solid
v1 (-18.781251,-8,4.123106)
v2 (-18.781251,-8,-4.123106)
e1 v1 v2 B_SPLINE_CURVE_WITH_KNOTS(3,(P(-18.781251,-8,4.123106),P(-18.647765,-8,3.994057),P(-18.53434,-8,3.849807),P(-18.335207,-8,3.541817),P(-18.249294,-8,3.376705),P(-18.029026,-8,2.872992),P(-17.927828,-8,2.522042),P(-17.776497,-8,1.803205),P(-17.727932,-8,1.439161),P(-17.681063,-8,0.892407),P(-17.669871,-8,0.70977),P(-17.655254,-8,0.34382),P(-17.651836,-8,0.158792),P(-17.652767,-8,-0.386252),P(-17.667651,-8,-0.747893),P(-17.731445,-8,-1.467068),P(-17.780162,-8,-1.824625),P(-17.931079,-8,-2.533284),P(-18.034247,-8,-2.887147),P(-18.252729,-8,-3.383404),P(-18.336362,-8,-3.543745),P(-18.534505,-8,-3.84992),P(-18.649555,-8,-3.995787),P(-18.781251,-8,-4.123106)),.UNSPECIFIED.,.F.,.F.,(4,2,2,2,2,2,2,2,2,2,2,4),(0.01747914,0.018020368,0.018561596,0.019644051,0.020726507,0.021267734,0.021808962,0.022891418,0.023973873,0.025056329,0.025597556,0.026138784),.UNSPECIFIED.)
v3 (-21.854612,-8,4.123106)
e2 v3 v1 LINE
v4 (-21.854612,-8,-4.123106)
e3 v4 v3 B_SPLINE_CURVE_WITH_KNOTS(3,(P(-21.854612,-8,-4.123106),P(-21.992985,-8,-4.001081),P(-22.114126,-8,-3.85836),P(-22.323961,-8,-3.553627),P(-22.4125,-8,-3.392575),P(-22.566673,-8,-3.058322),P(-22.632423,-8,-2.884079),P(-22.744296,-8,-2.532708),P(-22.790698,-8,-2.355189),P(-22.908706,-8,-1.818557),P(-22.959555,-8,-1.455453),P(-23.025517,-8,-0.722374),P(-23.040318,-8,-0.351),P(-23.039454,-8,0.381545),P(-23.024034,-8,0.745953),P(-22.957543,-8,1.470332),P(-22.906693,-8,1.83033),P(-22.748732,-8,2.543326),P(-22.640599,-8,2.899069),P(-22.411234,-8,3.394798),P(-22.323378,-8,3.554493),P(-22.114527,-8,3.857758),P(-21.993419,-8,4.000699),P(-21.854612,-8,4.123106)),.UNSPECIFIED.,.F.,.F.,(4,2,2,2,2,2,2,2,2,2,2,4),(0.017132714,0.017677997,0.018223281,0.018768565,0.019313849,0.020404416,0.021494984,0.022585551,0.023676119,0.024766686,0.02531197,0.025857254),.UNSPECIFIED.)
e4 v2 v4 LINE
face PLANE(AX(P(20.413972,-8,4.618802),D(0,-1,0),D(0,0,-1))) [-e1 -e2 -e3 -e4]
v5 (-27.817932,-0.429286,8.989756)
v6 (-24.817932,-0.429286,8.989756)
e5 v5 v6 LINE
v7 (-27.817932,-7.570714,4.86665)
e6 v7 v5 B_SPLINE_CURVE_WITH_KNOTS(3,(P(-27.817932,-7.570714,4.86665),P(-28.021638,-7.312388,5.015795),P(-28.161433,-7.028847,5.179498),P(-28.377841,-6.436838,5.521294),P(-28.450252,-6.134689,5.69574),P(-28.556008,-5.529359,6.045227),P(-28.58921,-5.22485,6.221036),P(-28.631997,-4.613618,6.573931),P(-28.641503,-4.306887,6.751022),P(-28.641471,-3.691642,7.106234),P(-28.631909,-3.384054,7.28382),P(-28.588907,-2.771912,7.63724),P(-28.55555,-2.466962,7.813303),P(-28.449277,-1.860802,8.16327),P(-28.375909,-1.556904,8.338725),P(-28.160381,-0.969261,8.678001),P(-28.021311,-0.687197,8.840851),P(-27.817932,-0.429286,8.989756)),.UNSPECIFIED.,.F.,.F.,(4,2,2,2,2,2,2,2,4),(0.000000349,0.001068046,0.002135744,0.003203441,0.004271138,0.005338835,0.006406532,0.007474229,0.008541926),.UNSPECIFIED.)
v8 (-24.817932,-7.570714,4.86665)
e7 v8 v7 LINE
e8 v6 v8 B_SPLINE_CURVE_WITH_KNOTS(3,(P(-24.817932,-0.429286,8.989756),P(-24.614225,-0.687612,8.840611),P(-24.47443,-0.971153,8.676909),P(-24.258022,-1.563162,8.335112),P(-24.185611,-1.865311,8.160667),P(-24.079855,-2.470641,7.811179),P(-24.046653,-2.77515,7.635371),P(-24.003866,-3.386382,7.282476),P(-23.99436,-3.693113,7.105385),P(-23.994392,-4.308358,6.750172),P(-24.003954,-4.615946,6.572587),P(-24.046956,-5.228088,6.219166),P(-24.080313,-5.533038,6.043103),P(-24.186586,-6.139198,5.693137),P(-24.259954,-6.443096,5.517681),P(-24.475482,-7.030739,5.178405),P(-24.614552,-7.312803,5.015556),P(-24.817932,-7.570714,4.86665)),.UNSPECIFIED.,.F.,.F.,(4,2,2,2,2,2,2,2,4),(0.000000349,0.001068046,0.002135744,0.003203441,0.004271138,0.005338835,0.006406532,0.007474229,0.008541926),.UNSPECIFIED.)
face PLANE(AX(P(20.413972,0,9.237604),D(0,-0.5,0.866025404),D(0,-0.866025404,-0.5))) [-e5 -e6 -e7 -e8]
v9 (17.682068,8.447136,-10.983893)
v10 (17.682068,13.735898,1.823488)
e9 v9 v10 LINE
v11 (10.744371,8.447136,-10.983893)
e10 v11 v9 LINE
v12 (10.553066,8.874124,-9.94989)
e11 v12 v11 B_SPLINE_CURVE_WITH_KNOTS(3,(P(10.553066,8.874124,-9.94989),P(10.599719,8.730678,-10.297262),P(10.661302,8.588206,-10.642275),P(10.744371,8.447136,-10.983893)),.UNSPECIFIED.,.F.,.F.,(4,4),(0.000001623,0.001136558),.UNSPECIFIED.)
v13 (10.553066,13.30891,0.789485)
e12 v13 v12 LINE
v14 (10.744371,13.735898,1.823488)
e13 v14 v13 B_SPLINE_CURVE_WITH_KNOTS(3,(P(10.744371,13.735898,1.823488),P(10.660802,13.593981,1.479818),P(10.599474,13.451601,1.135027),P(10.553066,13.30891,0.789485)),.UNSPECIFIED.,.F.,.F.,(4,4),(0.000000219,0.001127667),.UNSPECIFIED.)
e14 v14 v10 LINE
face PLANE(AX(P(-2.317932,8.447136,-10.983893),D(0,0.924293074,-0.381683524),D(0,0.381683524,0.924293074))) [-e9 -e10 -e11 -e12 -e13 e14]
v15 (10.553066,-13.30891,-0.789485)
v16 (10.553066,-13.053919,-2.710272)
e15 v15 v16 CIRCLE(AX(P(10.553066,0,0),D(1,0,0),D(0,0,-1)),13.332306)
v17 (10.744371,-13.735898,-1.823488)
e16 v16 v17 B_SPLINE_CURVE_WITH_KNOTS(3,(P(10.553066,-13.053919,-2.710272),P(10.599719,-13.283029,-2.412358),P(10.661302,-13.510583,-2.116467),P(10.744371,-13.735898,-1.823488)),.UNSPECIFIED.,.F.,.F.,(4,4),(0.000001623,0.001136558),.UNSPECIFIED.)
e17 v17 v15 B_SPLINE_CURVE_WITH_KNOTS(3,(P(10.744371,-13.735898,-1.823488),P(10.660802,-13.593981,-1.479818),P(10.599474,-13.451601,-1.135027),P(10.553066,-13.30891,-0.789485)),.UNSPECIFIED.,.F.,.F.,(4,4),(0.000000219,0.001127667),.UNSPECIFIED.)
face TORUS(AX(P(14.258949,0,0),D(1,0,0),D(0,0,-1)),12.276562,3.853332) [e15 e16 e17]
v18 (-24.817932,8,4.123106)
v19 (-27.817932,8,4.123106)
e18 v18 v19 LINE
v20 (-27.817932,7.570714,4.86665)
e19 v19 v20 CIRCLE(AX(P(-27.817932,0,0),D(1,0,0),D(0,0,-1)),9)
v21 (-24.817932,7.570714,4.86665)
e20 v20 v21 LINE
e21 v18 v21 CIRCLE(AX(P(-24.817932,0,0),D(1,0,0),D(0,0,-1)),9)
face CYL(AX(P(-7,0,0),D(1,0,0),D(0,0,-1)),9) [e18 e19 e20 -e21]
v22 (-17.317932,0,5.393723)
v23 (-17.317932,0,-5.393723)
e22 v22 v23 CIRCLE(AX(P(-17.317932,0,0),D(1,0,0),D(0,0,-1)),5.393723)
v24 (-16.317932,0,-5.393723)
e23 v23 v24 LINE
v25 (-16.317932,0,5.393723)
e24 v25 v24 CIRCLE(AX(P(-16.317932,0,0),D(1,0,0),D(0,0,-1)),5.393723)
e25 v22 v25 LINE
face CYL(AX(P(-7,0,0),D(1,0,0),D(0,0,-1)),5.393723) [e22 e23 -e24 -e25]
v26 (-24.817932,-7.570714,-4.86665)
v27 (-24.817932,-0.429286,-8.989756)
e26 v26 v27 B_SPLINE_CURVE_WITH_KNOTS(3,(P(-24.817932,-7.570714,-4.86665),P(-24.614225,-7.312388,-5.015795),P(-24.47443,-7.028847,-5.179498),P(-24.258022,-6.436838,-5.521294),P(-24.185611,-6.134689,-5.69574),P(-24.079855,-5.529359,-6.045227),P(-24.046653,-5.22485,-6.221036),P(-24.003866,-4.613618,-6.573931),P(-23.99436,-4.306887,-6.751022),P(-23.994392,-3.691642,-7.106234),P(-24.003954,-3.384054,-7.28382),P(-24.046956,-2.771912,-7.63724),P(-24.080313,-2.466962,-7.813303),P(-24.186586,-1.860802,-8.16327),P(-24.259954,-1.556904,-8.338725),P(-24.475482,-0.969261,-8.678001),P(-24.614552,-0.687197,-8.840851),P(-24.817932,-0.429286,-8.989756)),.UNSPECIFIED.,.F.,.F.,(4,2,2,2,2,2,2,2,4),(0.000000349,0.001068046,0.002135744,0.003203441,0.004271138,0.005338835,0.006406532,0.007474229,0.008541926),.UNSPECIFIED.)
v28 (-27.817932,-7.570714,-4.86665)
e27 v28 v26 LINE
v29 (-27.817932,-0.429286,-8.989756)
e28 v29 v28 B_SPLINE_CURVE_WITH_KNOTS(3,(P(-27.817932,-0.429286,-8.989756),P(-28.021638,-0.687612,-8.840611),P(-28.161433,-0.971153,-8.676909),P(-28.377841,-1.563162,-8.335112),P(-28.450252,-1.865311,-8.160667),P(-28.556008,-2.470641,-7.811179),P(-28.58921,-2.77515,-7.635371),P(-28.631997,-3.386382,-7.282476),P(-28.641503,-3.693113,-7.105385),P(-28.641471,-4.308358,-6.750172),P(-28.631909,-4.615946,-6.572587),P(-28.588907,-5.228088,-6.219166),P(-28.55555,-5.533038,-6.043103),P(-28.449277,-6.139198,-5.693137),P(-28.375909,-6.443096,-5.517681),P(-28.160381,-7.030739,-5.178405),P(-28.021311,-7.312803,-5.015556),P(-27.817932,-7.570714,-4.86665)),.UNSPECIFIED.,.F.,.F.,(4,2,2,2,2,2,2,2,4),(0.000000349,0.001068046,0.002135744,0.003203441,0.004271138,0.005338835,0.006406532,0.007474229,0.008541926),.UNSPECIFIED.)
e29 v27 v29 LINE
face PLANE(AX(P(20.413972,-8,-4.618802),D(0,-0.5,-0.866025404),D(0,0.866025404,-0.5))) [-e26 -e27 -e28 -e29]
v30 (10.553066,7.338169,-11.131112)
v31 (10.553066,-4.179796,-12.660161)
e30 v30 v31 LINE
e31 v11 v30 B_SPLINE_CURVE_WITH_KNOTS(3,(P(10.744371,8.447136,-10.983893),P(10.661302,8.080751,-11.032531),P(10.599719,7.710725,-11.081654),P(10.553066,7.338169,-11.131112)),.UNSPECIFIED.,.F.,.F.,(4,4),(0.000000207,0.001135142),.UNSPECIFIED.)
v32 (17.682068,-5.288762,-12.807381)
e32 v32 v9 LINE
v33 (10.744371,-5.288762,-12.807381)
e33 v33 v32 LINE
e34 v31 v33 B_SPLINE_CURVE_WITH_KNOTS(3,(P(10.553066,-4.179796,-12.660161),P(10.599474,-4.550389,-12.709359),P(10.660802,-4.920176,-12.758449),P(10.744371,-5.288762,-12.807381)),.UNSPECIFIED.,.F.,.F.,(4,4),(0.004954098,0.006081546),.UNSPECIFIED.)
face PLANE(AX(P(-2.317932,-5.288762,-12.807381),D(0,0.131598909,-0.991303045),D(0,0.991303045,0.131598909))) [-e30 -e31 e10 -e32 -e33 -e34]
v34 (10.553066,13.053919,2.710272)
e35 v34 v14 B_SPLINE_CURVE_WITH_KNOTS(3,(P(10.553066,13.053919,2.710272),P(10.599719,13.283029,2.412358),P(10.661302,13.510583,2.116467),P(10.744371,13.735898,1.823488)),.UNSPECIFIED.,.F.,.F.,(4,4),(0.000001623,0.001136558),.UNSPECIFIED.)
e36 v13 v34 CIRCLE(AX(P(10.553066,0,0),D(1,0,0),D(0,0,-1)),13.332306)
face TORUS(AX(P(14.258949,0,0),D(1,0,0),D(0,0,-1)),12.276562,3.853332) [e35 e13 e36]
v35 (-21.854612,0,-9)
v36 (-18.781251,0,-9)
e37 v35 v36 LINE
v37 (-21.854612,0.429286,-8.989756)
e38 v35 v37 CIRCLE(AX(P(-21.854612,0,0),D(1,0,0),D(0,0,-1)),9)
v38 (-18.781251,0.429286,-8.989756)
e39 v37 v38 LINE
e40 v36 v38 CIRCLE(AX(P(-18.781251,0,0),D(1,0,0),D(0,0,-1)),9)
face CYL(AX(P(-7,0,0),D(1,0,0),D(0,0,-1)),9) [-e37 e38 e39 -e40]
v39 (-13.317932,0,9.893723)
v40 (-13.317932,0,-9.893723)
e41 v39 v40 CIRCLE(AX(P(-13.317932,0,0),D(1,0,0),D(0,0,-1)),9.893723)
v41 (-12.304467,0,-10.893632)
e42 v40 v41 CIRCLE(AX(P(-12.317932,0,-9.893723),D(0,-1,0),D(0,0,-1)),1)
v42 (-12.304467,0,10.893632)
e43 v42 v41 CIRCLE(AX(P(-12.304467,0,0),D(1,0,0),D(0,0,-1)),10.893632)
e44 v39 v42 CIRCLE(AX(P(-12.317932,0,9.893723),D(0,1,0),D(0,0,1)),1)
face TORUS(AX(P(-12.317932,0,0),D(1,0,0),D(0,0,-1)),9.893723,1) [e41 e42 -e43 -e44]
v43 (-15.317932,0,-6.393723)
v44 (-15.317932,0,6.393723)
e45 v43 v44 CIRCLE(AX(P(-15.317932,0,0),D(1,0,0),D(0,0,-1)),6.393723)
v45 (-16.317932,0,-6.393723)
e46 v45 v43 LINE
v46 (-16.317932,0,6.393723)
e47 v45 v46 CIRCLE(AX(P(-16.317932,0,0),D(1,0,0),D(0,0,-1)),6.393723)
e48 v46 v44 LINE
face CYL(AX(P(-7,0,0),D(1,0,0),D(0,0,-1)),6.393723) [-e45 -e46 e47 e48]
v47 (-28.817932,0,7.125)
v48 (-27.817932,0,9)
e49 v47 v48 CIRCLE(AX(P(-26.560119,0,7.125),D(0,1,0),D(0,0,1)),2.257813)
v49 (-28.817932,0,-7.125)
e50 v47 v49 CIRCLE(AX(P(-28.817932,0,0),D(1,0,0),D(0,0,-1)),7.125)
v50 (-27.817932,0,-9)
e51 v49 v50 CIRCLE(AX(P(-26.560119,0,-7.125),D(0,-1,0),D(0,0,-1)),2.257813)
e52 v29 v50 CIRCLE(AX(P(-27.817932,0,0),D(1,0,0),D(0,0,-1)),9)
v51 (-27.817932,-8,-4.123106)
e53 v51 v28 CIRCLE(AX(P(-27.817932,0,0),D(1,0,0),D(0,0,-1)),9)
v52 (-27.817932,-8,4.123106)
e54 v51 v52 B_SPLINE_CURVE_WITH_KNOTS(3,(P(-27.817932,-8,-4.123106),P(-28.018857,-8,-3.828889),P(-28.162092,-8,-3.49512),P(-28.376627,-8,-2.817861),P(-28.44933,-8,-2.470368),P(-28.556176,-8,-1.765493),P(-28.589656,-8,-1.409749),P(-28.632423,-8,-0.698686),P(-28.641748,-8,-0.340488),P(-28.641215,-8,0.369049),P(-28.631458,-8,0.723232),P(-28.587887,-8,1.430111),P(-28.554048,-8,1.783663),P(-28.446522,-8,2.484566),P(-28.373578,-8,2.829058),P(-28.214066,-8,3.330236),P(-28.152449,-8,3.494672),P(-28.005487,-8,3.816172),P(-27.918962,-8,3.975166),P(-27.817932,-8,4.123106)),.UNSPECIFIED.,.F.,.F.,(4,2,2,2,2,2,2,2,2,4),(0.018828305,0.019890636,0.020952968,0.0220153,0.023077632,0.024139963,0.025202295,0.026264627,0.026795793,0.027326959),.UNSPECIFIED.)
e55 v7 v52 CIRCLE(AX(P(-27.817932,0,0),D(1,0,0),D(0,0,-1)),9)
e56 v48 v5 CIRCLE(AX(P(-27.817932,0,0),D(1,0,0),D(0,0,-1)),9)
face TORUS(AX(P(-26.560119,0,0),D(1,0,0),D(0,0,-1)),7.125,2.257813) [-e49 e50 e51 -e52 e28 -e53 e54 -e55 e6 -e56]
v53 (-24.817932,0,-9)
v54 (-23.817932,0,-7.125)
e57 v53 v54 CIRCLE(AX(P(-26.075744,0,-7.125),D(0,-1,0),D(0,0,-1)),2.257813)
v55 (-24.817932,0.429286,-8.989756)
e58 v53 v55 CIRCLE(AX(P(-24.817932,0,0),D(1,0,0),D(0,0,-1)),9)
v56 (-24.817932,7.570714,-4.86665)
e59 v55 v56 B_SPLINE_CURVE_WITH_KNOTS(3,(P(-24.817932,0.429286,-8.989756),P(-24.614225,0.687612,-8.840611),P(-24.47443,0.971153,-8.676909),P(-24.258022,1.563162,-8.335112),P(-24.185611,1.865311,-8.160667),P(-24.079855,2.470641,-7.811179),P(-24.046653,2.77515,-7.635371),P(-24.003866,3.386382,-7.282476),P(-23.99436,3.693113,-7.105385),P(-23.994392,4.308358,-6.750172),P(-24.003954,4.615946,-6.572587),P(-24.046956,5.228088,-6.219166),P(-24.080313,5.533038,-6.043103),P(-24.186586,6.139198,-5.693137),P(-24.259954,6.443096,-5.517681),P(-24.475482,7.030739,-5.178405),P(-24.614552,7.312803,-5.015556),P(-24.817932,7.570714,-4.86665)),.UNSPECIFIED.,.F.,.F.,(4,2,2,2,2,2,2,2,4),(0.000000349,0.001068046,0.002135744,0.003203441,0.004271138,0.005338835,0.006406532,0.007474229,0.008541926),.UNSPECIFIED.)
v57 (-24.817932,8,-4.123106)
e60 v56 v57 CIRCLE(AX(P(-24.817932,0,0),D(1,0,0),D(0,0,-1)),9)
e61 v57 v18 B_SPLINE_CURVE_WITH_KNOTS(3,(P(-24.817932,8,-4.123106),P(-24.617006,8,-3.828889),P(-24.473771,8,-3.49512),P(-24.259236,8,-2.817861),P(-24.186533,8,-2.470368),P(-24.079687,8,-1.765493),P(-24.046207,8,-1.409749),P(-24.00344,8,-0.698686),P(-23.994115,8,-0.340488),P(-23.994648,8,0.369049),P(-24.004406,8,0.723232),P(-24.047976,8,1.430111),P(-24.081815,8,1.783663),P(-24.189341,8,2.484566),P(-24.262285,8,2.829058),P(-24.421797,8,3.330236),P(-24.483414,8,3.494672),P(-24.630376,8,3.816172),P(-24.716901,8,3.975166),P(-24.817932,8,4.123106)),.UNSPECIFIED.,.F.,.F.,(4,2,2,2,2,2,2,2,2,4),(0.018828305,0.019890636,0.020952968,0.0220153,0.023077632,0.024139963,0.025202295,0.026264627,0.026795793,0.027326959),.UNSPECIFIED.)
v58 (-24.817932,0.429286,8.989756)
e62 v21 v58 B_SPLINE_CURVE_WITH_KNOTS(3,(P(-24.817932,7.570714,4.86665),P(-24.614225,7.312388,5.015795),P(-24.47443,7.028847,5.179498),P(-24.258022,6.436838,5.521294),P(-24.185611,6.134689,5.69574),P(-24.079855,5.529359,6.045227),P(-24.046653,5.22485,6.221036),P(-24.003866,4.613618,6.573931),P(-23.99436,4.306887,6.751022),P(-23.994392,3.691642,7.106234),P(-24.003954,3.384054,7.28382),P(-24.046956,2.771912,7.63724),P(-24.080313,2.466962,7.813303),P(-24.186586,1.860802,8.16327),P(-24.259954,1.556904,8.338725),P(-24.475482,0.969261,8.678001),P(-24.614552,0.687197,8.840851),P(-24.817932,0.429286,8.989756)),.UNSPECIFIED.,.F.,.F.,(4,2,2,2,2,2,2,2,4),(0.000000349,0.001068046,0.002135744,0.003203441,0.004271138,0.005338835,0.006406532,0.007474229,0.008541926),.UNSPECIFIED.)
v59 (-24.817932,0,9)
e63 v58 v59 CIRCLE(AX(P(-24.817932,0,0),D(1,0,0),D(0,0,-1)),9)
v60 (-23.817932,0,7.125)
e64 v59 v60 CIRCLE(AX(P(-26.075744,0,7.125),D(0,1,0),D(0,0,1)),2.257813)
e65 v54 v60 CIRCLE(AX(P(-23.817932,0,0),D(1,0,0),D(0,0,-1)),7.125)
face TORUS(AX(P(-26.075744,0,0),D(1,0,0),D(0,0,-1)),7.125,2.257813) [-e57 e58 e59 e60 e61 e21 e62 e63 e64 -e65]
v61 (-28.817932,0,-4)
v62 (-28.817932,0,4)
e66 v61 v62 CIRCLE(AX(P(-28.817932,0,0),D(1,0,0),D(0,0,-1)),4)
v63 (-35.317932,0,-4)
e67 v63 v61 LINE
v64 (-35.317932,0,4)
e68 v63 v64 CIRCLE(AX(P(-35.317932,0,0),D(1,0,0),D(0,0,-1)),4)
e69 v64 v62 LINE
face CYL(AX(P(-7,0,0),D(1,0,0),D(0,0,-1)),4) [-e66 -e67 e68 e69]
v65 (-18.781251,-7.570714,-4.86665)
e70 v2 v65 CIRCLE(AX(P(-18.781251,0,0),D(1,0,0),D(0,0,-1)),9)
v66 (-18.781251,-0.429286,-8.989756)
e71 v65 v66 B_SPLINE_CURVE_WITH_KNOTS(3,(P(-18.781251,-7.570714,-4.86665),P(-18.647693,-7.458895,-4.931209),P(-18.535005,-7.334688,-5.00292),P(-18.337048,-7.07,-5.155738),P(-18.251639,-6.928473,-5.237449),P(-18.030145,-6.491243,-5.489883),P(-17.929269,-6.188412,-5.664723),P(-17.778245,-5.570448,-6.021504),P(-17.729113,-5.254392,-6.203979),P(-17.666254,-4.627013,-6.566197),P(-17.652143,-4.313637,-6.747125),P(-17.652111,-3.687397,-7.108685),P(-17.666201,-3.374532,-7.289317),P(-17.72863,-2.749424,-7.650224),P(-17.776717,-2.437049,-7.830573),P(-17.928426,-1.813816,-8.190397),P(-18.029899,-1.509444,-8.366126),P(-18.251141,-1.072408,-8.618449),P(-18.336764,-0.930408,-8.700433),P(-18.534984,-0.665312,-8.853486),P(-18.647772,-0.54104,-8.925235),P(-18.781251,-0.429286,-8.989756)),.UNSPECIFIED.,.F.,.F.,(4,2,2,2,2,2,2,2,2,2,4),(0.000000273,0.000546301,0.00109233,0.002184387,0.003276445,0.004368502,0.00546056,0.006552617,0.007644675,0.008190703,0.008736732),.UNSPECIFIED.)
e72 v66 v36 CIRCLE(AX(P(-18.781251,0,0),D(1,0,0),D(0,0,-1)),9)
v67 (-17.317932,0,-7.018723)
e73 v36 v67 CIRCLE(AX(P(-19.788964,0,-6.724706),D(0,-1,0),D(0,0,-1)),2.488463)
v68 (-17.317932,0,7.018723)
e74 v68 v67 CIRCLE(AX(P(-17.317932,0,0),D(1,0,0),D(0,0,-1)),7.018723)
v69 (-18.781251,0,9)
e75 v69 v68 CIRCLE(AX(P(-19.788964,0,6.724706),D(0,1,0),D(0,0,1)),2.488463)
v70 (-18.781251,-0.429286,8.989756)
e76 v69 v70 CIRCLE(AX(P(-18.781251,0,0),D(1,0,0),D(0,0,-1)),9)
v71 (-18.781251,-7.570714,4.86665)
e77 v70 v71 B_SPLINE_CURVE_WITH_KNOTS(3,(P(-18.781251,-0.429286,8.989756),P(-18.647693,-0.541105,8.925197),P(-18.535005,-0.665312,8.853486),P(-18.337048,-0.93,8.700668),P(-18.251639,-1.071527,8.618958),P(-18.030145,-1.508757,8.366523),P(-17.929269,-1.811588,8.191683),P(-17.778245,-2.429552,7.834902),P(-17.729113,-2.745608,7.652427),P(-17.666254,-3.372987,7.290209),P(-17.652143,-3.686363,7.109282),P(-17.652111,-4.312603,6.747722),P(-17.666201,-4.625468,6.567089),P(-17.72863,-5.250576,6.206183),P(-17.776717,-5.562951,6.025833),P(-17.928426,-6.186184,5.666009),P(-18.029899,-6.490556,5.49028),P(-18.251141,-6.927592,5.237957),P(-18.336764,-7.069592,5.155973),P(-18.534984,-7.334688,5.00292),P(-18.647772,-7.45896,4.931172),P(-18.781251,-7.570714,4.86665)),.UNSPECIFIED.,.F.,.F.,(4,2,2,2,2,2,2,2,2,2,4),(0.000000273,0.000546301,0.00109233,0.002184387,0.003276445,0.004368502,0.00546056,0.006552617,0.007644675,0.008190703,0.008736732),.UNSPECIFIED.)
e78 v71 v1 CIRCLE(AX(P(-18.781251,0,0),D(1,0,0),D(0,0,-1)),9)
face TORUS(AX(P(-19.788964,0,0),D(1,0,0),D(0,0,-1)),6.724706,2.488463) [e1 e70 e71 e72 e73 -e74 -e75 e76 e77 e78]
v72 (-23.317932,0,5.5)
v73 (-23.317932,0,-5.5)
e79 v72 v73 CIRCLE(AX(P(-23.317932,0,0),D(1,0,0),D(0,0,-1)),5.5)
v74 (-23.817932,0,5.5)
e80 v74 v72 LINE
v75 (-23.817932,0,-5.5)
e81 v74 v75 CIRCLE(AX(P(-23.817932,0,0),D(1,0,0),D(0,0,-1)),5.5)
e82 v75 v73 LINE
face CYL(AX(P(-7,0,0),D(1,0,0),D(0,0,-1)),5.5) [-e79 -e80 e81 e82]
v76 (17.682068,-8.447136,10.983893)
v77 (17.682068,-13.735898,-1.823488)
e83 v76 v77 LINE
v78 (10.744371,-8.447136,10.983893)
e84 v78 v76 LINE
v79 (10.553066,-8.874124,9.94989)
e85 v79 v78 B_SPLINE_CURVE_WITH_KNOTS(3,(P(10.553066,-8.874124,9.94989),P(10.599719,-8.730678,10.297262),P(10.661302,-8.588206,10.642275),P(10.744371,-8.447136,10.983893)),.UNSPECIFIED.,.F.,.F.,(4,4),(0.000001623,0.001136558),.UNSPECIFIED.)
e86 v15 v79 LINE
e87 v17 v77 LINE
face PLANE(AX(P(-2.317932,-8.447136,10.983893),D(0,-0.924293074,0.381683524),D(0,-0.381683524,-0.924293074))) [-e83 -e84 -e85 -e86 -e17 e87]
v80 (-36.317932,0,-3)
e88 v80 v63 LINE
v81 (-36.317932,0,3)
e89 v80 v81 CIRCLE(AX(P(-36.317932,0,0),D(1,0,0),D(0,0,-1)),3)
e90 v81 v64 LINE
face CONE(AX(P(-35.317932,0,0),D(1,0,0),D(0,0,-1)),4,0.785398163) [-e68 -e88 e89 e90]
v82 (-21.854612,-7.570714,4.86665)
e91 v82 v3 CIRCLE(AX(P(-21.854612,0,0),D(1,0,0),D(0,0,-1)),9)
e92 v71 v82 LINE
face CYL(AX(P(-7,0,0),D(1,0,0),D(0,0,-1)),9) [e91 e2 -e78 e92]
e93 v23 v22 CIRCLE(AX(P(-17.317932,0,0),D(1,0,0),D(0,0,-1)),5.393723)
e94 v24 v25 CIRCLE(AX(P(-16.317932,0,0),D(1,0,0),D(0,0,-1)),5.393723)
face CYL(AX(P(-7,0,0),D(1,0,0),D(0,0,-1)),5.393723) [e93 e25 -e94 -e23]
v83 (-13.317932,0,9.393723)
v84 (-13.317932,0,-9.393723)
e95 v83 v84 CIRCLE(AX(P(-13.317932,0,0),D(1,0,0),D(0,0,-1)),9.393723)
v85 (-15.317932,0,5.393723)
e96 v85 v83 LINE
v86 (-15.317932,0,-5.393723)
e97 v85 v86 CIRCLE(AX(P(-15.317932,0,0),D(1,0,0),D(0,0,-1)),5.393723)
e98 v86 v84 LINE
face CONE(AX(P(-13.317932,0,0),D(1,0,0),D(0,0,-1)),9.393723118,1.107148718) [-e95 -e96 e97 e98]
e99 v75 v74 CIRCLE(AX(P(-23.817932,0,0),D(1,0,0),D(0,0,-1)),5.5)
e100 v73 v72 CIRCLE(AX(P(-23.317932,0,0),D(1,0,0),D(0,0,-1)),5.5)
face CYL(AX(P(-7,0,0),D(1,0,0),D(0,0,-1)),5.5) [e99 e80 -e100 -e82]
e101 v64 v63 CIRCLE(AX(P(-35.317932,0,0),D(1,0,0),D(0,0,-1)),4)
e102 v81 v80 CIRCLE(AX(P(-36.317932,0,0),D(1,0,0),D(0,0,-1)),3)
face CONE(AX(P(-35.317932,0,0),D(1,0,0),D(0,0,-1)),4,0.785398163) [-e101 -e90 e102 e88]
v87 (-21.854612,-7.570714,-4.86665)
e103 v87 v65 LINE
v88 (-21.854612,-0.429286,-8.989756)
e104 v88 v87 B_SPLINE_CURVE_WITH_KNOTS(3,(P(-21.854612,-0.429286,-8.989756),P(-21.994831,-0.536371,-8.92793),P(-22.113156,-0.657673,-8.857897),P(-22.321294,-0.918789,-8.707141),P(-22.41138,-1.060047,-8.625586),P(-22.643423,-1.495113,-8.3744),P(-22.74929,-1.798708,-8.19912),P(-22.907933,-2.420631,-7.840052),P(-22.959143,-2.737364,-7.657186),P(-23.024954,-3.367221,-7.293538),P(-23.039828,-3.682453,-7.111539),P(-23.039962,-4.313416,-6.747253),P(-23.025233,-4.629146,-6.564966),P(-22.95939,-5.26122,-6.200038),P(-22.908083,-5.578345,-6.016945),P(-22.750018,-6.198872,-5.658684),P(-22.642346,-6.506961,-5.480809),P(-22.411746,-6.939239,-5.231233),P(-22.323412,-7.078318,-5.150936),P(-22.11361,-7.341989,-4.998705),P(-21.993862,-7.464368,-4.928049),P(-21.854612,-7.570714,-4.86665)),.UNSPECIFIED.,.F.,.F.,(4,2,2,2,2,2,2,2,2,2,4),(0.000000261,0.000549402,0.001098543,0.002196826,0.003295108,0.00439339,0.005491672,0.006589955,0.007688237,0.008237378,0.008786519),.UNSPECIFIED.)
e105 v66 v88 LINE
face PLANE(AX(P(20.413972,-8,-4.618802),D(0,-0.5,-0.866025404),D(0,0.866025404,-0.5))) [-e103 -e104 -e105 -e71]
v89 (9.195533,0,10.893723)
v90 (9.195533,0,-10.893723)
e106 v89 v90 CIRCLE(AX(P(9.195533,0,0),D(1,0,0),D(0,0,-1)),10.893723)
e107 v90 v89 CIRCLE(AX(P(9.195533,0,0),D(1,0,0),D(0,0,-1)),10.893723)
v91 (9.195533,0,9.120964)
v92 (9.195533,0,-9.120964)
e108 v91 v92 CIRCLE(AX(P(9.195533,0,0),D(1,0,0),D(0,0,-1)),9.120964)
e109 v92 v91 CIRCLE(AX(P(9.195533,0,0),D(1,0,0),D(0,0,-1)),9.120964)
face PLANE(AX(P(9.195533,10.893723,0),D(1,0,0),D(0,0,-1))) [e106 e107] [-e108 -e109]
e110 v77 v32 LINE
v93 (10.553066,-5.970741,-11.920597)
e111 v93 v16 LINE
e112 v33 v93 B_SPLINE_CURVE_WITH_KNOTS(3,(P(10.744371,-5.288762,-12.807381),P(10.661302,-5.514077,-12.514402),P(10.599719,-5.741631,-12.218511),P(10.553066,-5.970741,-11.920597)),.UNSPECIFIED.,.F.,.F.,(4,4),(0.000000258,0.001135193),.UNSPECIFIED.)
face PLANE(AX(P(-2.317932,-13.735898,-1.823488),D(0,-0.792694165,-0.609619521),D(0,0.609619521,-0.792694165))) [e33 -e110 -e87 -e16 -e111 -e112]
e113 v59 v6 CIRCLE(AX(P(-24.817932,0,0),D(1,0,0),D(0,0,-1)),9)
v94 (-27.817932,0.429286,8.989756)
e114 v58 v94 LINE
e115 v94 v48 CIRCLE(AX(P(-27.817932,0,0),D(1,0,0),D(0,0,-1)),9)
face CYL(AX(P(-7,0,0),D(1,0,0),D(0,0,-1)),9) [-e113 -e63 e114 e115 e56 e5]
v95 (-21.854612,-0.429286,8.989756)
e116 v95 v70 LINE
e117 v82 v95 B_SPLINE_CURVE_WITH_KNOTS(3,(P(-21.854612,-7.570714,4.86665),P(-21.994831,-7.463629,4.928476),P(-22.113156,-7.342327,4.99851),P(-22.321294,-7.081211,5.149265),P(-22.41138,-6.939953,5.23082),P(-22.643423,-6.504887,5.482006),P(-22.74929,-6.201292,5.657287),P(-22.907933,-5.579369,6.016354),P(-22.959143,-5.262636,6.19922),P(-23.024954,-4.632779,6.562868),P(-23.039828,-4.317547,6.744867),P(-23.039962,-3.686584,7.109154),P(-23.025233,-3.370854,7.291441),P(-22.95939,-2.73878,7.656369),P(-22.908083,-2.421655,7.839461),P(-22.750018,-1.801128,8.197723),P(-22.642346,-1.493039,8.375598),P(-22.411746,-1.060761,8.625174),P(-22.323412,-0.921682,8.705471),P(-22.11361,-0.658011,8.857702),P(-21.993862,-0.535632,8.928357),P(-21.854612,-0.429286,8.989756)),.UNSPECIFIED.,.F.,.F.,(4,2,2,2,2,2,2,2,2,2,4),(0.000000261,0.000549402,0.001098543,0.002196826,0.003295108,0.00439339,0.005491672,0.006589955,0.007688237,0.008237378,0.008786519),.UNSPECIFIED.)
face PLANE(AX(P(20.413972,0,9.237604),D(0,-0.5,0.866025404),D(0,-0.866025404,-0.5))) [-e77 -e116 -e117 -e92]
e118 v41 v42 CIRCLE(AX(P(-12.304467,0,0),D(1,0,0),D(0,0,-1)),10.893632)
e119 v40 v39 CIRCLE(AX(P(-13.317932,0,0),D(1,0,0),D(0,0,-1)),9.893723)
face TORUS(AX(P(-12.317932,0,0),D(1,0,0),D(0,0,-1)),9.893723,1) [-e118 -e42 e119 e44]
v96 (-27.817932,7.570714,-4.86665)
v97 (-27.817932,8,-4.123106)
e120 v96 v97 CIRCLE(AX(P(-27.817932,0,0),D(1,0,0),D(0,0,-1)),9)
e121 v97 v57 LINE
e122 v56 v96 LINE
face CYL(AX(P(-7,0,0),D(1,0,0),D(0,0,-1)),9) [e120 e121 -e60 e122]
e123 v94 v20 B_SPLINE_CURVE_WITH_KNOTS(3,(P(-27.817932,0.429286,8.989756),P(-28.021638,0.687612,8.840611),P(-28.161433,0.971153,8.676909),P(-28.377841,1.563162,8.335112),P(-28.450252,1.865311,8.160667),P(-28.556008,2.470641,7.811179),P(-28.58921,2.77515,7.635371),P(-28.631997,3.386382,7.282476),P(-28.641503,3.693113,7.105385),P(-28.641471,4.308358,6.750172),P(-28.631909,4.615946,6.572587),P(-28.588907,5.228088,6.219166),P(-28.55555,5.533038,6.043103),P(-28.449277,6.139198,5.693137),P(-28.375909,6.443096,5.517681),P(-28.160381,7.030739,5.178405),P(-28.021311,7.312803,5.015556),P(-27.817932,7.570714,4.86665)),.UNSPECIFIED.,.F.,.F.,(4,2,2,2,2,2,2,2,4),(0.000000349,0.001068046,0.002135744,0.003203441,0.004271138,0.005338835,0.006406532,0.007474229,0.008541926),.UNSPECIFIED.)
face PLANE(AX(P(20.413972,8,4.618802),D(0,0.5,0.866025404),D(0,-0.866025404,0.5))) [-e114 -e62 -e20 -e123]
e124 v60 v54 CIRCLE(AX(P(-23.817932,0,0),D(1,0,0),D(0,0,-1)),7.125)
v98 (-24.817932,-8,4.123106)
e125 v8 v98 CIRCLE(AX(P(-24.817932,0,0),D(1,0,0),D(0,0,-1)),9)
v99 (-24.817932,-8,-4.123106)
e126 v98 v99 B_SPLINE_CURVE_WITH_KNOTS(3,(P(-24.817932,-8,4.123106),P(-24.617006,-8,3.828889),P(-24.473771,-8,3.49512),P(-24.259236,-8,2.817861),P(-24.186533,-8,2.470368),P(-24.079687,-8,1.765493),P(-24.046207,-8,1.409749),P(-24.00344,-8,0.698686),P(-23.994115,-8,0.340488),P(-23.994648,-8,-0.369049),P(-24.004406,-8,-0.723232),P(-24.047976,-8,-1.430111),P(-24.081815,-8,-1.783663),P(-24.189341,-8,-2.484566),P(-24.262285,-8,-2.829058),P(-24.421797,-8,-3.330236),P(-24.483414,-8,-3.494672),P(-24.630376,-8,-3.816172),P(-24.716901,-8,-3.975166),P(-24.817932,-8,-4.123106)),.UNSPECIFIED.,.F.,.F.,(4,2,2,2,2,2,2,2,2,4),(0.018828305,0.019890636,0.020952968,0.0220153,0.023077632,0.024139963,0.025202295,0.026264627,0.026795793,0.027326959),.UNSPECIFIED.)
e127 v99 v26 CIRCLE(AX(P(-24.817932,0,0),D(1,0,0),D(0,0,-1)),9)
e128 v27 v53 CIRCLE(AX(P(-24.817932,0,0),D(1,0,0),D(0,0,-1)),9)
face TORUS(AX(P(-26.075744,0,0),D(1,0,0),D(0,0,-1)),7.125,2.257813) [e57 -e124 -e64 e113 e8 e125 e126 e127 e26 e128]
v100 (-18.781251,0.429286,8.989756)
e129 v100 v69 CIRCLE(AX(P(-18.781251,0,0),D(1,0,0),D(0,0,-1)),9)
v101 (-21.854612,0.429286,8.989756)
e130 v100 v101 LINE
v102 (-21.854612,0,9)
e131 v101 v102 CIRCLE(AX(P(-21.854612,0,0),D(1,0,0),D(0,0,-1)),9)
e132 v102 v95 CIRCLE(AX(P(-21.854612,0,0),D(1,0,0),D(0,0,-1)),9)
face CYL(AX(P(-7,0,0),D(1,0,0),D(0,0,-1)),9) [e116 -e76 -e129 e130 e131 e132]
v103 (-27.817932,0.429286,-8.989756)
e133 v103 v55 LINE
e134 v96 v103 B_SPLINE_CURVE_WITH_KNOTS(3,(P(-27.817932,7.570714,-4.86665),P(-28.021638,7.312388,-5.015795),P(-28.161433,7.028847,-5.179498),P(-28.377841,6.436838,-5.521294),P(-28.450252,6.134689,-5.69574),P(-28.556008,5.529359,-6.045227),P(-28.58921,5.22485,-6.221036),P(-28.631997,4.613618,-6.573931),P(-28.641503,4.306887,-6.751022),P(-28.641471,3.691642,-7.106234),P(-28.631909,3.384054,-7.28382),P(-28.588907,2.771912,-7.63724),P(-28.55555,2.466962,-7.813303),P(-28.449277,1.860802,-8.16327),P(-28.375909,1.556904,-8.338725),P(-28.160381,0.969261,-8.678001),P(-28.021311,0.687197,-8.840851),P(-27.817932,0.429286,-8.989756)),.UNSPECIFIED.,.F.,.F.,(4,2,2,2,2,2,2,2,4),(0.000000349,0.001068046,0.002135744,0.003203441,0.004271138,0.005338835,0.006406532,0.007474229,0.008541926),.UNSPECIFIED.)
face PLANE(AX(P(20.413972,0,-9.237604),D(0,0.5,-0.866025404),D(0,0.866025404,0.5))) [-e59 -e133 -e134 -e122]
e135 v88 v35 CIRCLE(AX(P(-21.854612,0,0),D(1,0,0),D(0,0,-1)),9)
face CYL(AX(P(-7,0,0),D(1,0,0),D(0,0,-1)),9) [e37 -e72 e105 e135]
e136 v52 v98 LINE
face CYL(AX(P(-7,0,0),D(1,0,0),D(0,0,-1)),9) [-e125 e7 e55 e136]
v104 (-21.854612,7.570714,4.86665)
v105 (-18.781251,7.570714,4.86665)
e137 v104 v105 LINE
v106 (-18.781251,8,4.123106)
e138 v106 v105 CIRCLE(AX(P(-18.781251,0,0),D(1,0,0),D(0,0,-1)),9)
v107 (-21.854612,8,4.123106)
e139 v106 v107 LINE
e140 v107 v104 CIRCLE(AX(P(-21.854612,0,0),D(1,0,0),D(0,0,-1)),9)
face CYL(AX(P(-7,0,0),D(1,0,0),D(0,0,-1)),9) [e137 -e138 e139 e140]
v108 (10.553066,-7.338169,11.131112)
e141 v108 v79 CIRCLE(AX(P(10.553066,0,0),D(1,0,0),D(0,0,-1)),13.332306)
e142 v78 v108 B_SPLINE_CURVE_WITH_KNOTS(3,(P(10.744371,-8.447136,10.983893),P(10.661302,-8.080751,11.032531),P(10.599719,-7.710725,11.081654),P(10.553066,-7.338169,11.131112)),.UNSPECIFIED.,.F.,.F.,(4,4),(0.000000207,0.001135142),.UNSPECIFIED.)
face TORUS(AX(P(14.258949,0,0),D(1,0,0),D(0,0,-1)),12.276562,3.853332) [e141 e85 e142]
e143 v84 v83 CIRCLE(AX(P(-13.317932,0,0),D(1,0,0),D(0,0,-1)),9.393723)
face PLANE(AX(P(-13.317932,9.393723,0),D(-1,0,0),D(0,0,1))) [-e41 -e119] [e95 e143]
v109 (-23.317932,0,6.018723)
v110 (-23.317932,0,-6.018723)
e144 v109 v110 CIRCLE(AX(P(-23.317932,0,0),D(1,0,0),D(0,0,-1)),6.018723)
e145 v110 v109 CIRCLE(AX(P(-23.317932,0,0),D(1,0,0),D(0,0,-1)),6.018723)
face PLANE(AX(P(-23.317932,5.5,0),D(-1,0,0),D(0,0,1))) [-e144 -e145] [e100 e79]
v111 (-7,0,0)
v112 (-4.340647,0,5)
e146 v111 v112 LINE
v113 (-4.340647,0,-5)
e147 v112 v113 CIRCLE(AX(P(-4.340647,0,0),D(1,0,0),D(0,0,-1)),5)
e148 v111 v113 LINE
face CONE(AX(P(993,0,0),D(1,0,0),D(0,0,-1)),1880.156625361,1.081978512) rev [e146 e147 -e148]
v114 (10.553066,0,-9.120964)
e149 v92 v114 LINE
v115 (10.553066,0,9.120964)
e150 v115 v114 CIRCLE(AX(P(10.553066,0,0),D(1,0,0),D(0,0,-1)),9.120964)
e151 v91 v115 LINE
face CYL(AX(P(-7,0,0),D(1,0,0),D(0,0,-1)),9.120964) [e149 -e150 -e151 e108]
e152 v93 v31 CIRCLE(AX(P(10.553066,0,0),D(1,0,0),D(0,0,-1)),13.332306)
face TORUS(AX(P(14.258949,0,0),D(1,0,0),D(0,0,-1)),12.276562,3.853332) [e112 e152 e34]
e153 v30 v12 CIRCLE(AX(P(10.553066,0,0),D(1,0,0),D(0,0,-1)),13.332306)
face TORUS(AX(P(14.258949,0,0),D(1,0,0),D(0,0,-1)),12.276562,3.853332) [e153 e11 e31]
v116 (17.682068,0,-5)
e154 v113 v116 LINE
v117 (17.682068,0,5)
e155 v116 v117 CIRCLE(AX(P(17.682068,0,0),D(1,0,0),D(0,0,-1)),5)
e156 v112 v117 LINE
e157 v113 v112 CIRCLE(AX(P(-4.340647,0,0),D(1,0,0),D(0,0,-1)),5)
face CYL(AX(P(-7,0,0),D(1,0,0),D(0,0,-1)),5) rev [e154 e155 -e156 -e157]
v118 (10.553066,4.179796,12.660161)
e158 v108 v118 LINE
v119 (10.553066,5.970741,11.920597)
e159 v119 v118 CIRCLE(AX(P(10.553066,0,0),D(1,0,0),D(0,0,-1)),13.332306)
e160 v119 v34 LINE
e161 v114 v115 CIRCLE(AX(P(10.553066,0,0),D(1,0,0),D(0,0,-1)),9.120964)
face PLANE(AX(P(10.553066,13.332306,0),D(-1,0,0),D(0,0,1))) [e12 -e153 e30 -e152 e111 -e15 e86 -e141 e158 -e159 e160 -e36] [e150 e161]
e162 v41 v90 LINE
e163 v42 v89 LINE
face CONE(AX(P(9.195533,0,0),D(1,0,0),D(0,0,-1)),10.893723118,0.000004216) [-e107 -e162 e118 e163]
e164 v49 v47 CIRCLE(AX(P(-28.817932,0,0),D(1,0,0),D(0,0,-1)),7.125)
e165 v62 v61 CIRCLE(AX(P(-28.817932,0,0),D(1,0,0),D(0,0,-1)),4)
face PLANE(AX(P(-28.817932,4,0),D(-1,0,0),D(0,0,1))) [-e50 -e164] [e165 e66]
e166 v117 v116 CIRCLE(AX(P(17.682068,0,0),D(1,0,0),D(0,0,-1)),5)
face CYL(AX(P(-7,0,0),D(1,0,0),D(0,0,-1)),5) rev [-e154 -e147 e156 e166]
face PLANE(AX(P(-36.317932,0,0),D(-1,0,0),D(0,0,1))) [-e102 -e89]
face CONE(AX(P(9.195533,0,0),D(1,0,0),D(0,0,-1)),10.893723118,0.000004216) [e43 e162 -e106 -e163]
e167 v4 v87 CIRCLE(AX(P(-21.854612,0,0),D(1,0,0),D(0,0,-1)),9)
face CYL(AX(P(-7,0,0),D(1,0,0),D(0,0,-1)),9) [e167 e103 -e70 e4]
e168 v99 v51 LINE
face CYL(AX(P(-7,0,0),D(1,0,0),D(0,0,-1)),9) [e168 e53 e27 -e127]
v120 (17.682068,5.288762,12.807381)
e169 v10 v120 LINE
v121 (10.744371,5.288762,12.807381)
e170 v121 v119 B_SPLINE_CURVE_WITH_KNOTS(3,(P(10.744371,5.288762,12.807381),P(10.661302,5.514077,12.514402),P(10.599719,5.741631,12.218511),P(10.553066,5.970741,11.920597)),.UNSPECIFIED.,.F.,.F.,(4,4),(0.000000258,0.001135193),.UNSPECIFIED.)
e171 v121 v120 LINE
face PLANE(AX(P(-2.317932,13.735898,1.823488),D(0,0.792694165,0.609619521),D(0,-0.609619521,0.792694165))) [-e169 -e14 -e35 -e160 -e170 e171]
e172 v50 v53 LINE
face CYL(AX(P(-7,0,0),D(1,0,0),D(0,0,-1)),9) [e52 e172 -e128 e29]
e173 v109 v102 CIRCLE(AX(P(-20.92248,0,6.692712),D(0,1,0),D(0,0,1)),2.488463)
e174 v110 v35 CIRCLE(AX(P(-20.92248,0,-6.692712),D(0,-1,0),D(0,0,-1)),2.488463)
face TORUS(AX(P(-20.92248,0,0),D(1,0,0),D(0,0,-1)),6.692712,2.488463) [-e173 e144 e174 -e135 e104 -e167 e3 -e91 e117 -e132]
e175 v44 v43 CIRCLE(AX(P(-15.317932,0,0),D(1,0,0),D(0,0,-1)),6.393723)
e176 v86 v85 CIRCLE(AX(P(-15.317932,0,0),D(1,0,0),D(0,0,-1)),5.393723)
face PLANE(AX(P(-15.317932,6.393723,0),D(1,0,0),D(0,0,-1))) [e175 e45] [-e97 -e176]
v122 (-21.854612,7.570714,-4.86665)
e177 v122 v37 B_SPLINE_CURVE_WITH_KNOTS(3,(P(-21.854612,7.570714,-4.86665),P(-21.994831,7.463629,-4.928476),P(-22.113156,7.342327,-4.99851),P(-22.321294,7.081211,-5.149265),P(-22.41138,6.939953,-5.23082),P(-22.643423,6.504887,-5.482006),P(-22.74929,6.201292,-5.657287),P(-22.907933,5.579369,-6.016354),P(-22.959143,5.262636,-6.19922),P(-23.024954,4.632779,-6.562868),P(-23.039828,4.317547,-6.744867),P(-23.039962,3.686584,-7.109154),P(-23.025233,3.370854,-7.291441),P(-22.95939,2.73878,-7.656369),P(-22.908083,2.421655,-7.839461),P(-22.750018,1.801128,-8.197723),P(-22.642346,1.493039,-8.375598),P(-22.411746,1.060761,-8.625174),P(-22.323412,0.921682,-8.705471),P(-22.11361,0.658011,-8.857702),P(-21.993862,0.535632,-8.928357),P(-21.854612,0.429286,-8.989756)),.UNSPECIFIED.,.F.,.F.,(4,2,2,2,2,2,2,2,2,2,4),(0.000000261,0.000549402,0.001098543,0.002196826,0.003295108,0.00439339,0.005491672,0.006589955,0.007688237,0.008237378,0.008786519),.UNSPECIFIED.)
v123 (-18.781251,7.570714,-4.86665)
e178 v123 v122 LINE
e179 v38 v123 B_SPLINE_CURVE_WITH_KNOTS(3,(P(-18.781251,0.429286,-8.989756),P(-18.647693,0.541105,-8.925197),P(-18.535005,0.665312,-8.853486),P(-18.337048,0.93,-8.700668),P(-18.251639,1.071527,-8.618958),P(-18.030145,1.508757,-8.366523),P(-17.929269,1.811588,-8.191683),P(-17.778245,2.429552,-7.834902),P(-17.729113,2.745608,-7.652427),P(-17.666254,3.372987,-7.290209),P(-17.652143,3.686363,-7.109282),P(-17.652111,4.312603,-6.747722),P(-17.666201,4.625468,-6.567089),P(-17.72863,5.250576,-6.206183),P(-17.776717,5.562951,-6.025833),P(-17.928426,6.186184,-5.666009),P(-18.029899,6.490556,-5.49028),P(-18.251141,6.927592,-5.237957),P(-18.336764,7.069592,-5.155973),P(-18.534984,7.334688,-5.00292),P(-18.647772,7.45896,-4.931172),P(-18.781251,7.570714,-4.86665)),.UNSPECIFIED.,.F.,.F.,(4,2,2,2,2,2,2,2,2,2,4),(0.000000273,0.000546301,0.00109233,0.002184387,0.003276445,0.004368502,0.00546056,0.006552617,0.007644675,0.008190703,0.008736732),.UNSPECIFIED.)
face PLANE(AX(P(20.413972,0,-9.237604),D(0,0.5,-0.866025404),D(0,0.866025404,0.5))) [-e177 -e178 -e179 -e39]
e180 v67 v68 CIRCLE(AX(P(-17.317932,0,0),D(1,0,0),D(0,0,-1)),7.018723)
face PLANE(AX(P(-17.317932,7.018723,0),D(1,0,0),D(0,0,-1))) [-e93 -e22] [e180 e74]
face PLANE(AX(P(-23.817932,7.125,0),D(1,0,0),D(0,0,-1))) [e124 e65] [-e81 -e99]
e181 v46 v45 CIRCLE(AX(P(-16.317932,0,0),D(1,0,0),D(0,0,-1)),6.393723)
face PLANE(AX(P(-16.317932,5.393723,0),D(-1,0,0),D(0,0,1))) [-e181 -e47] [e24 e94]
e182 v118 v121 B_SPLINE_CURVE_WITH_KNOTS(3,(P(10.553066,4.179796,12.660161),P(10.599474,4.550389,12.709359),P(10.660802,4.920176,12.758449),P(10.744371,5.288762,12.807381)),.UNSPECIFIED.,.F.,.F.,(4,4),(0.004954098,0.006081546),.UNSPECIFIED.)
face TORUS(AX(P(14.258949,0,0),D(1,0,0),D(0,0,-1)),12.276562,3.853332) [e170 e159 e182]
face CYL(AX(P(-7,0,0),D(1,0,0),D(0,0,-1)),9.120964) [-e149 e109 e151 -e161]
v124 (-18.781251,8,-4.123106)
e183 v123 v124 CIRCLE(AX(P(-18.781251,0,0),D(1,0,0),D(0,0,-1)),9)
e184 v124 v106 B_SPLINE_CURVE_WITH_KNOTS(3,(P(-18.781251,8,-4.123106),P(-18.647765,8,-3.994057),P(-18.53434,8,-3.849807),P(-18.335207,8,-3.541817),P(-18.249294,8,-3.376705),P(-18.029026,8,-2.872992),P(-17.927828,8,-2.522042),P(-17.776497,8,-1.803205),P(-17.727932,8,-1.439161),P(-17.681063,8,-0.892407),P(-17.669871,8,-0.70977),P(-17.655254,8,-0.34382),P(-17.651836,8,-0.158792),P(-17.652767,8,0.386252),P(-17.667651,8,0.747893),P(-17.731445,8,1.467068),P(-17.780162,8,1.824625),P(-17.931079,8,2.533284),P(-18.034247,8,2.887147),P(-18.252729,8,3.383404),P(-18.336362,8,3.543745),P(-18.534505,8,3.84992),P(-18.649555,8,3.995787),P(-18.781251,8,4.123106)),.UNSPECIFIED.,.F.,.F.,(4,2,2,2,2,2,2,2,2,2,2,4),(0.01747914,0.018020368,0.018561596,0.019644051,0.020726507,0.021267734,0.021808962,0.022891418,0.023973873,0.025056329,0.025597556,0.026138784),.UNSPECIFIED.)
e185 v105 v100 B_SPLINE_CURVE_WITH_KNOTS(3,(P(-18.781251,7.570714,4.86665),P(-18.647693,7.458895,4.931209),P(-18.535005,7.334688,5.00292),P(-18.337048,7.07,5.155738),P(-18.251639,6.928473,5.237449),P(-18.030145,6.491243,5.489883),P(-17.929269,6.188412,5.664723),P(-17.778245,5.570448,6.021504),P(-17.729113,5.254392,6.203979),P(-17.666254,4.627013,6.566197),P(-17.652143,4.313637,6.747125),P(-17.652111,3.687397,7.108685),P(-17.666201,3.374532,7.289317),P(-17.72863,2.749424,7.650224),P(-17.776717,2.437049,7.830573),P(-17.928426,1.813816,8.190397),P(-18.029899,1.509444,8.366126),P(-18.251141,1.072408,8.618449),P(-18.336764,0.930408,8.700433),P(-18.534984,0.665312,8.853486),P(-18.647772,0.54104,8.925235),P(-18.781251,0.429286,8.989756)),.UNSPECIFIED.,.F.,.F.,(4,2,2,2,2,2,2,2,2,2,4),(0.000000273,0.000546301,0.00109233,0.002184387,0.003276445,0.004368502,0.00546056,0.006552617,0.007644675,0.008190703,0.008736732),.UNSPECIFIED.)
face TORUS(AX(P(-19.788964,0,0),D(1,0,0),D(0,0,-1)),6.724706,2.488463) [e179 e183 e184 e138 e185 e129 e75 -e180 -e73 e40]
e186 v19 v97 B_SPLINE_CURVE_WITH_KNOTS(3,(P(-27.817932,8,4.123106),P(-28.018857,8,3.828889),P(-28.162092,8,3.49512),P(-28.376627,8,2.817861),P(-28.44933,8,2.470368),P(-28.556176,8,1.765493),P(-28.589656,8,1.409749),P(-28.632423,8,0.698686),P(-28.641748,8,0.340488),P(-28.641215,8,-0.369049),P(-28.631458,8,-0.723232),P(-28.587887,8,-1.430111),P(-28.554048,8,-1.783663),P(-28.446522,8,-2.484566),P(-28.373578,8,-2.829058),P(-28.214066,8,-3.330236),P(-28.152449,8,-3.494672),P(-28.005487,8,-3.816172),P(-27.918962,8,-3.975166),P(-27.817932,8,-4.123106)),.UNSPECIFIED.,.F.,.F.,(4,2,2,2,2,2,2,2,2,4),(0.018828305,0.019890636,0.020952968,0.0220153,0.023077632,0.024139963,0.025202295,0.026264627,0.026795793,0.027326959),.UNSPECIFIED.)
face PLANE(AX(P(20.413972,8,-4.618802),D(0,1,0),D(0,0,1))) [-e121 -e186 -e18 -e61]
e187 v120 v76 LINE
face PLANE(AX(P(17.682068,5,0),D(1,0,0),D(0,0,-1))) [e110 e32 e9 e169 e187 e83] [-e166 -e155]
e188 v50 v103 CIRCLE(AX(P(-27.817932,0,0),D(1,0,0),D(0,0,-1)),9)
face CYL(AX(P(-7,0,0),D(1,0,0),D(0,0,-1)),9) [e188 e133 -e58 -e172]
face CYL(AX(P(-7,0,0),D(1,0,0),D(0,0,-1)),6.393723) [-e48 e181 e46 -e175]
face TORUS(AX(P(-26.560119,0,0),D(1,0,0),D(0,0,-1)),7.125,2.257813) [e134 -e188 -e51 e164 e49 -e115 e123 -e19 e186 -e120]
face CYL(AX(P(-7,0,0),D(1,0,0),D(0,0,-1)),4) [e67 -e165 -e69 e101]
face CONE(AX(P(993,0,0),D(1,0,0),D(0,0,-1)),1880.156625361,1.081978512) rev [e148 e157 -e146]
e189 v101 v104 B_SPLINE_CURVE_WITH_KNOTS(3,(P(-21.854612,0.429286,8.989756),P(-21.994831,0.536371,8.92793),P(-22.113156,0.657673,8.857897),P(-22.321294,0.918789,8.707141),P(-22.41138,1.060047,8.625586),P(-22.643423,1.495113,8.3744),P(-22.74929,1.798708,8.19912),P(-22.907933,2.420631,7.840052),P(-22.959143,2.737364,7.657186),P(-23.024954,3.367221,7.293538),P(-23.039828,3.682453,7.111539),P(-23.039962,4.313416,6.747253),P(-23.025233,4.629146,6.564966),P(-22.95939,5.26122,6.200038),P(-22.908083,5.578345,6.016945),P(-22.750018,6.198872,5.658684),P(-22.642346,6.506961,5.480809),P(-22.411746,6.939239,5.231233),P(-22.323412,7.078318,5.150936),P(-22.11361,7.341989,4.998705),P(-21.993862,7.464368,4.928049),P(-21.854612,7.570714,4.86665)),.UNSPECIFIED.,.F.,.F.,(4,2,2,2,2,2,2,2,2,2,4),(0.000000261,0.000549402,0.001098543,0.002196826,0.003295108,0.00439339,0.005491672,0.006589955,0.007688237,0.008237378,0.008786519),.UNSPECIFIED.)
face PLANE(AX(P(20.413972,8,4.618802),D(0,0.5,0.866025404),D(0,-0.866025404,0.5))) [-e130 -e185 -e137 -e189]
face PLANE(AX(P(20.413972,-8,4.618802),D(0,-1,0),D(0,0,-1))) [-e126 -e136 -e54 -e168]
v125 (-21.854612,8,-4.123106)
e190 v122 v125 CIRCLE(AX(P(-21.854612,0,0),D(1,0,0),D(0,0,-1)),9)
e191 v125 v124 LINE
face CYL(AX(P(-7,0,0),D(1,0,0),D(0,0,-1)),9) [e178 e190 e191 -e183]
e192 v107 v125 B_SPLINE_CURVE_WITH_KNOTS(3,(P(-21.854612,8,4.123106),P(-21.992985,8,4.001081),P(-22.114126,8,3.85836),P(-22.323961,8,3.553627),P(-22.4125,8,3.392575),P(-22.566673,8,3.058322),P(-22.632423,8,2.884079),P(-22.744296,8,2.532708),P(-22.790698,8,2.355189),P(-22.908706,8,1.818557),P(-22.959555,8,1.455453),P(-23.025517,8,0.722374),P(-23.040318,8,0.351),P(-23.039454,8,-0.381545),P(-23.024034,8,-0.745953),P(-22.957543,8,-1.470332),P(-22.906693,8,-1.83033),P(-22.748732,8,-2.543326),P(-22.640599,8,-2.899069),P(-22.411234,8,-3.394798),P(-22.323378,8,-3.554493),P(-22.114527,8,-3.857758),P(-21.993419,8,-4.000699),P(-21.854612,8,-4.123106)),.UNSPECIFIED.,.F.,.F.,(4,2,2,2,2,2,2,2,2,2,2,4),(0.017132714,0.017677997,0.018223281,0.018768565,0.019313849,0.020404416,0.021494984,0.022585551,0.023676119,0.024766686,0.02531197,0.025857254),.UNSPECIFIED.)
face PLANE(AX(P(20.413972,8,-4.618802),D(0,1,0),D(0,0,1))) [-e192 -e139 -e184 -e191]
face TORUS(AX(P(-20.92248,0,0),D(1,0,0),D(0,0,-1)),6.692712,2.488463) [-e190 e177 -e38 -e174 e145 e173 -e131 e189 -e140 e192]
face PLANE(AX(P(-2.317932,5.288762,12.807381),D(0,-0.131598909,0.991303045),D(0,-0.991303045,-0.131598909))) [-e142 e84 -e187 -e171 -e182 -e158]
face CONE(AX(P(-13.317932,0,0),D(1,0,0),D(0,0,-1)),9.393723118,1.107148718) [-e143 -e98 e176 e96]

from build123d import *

# Parameters (mm, degrees)
CUT_EXTRUDE1_REACH = 53.794
SKETCH2_R          = 13.340242397
SKETCH4_OUTSIDE_W  = 48.398
SKETCH4_OUTSIDE_H  = 48.398
CUT_EXTRUDE3_DEPTH = 20


with BuildPart() as part:
    # Sketch1 → Revolve1 (revolve)
    with BuildSketch(Plane.XY, mode=Mode.PRIVATE) as revolve1_sk:
        with BuildLine():
            Line((10.553065695, 13.332305779), (10.553065695, 9.120964454))
            Line((10.553065695, 9.120964454), (9.195532772, 9.120964454))
            Line((9.195532772, 9.120964454), (9.195532772, 10.893723118))
            Line((9.195532772, 10.893723118), (-12.304467227, 10.89363247))
            ThreePointArc((-12.304467227, 10.89363247), (-13.020261836, 10.605574336), (-13.317931541, 9.893723118))
            Line((-13.317931541, 9.893723118), (-13.317931541, 9.393723118))
            Line((-13.317931541, 9.393723118), (-15.317931541, 5.393723118))
            Line((-15.317931541, 5.393723118), (-15.317931541, 6.393723118))
            Line((-15.317931541, 6.393723118), (-16.317931541, 6.393723118))
            Line((-16.317931541, 6.393723118), (-16.317931541, 5.393723118))
            Line((-16.317931541, 5.393723118), (-17.317931541, 5.393723118))
            Line((-17.317931541, 5.393723118), (-17.317931541, 7.018723118))
            ThreePointArc((-17.317931541, 7.018723118), (-17.787269372, 8.203105819), (-18.781251286, 9))
            Line((-18.781251286, 9), (-21.854611796, 9))
            ThreePointArc((-21.854611796, 9), (-23.156356824, 7.789180206), (-23.317931541, 6.018723118))
            Line((-23.317931541, 6.018723118), (-23.317931541, 5.5))
            Line((-23.317931541, 5.5), (-23.81793154, 5.5))
            Line((-23.81793154, 5.5), (-23.81793154, 7.125))
            ThreePointArc((-23.81793154, 7.125), (-24.08355654, 8.1875), (-24.81793154, 9))
            Line((-24.81793154, 9), (-27.81793154, 9))
            ThreePointArc((-27.81793154, 9), (-28.55230654, 8.1875), (-28.81793154, 7.125))
            Line((-28.81793154, 7.125), (-28.81793154, 4))
            Line((-28.81793154, 4), (-35.317931541, 4))
            Line((-35.317931541, 4), (-36.317931541, 3))
            Line((-36.317931541, 3), (-36.317931541, 0))
            Line((-36.317931541, 0), (-7, 0))
            Line((-7, 0), (-4.340647086, 5))
            Line((-4.340647086, 5), (17.682068459, 5))
            Line((17.682068459, 5), (17.682068459, 14.045862297))
            ThreePointArc((17.682068459, 14.045862297), (13.875178985, 16.110735773), (10.553065695, 13.332305779))
        make_face()
    revolve(revolve1_sk.sketch.rotate(Axis((-7, 0, 0), (-1, 0, 0)), 90), axis=Axis((-7, 0, 0), (-1, 0, 0)))

    # Cut-Extrude1: up to this face of the body (flat: up to its plane)
    cut_extrude1_end = Plane(part.part.faces().sort_by_distance((-17.317931541, 0, 5.592242587))[0])
    # Sketch2 → Cut-Extrude1 (cut, up to the picked face)
    with BuildSketch(Plane.ZY.offset(28.81793154), mode=Mode.PRIVATE) as cut_extrude1_sk1:
        Circle(SKETCH2_R)
        Polygon((-4.618802154, 8), (4.618802154, 8), (9.237604307, 0), (4.618802154, -8), (-4.618802154, -8), (-9.237604307, 0), align=None, mode=Mode.SUBTRACT)
    cut_extrude1_tool1 = split(extrude(cut_extrude1_sk1.sketch, amount=-CUT_EXTRUDE1_REACH, mode=Mode.PRIVATE), bisect_by=cut_extrude1_end, keep=Keep.BOTH, mode=Mode.PRIVATE)
    add(cut_extrude1_tool1.solids().sort_by(Axis((-28.817932, 0, -12.962923), (1, 0, 0)))[0], mode=Mode.SUBTRACT)

    # Sketch4 outside → Cut-Extrude3 (cut)
    with BuildSketch(Plane(origin=(17.682068459, 0, 0), x_dir=(0, 0, -1), z_dir=(1, 0, 0))):
        Rectangle(SKETCH4_OUTSIDE_W, SKETCH4_OUTSIDE_H)
        Polygon((12.807380528, -5.288762048), (10.983892553, 8.447135869), (-1.823487976, 13.735897918), (-12.807380528, 5.288762048), (-10.983892553, -8.447135869), (1.823487976, -13.735897918), align=None, mode=Mode.SUBTRACT)
    extrude(amount=-CUT_EXTRUDE3_DEPTH, mode=Mode.SUBTRACT)


solid = part.part
